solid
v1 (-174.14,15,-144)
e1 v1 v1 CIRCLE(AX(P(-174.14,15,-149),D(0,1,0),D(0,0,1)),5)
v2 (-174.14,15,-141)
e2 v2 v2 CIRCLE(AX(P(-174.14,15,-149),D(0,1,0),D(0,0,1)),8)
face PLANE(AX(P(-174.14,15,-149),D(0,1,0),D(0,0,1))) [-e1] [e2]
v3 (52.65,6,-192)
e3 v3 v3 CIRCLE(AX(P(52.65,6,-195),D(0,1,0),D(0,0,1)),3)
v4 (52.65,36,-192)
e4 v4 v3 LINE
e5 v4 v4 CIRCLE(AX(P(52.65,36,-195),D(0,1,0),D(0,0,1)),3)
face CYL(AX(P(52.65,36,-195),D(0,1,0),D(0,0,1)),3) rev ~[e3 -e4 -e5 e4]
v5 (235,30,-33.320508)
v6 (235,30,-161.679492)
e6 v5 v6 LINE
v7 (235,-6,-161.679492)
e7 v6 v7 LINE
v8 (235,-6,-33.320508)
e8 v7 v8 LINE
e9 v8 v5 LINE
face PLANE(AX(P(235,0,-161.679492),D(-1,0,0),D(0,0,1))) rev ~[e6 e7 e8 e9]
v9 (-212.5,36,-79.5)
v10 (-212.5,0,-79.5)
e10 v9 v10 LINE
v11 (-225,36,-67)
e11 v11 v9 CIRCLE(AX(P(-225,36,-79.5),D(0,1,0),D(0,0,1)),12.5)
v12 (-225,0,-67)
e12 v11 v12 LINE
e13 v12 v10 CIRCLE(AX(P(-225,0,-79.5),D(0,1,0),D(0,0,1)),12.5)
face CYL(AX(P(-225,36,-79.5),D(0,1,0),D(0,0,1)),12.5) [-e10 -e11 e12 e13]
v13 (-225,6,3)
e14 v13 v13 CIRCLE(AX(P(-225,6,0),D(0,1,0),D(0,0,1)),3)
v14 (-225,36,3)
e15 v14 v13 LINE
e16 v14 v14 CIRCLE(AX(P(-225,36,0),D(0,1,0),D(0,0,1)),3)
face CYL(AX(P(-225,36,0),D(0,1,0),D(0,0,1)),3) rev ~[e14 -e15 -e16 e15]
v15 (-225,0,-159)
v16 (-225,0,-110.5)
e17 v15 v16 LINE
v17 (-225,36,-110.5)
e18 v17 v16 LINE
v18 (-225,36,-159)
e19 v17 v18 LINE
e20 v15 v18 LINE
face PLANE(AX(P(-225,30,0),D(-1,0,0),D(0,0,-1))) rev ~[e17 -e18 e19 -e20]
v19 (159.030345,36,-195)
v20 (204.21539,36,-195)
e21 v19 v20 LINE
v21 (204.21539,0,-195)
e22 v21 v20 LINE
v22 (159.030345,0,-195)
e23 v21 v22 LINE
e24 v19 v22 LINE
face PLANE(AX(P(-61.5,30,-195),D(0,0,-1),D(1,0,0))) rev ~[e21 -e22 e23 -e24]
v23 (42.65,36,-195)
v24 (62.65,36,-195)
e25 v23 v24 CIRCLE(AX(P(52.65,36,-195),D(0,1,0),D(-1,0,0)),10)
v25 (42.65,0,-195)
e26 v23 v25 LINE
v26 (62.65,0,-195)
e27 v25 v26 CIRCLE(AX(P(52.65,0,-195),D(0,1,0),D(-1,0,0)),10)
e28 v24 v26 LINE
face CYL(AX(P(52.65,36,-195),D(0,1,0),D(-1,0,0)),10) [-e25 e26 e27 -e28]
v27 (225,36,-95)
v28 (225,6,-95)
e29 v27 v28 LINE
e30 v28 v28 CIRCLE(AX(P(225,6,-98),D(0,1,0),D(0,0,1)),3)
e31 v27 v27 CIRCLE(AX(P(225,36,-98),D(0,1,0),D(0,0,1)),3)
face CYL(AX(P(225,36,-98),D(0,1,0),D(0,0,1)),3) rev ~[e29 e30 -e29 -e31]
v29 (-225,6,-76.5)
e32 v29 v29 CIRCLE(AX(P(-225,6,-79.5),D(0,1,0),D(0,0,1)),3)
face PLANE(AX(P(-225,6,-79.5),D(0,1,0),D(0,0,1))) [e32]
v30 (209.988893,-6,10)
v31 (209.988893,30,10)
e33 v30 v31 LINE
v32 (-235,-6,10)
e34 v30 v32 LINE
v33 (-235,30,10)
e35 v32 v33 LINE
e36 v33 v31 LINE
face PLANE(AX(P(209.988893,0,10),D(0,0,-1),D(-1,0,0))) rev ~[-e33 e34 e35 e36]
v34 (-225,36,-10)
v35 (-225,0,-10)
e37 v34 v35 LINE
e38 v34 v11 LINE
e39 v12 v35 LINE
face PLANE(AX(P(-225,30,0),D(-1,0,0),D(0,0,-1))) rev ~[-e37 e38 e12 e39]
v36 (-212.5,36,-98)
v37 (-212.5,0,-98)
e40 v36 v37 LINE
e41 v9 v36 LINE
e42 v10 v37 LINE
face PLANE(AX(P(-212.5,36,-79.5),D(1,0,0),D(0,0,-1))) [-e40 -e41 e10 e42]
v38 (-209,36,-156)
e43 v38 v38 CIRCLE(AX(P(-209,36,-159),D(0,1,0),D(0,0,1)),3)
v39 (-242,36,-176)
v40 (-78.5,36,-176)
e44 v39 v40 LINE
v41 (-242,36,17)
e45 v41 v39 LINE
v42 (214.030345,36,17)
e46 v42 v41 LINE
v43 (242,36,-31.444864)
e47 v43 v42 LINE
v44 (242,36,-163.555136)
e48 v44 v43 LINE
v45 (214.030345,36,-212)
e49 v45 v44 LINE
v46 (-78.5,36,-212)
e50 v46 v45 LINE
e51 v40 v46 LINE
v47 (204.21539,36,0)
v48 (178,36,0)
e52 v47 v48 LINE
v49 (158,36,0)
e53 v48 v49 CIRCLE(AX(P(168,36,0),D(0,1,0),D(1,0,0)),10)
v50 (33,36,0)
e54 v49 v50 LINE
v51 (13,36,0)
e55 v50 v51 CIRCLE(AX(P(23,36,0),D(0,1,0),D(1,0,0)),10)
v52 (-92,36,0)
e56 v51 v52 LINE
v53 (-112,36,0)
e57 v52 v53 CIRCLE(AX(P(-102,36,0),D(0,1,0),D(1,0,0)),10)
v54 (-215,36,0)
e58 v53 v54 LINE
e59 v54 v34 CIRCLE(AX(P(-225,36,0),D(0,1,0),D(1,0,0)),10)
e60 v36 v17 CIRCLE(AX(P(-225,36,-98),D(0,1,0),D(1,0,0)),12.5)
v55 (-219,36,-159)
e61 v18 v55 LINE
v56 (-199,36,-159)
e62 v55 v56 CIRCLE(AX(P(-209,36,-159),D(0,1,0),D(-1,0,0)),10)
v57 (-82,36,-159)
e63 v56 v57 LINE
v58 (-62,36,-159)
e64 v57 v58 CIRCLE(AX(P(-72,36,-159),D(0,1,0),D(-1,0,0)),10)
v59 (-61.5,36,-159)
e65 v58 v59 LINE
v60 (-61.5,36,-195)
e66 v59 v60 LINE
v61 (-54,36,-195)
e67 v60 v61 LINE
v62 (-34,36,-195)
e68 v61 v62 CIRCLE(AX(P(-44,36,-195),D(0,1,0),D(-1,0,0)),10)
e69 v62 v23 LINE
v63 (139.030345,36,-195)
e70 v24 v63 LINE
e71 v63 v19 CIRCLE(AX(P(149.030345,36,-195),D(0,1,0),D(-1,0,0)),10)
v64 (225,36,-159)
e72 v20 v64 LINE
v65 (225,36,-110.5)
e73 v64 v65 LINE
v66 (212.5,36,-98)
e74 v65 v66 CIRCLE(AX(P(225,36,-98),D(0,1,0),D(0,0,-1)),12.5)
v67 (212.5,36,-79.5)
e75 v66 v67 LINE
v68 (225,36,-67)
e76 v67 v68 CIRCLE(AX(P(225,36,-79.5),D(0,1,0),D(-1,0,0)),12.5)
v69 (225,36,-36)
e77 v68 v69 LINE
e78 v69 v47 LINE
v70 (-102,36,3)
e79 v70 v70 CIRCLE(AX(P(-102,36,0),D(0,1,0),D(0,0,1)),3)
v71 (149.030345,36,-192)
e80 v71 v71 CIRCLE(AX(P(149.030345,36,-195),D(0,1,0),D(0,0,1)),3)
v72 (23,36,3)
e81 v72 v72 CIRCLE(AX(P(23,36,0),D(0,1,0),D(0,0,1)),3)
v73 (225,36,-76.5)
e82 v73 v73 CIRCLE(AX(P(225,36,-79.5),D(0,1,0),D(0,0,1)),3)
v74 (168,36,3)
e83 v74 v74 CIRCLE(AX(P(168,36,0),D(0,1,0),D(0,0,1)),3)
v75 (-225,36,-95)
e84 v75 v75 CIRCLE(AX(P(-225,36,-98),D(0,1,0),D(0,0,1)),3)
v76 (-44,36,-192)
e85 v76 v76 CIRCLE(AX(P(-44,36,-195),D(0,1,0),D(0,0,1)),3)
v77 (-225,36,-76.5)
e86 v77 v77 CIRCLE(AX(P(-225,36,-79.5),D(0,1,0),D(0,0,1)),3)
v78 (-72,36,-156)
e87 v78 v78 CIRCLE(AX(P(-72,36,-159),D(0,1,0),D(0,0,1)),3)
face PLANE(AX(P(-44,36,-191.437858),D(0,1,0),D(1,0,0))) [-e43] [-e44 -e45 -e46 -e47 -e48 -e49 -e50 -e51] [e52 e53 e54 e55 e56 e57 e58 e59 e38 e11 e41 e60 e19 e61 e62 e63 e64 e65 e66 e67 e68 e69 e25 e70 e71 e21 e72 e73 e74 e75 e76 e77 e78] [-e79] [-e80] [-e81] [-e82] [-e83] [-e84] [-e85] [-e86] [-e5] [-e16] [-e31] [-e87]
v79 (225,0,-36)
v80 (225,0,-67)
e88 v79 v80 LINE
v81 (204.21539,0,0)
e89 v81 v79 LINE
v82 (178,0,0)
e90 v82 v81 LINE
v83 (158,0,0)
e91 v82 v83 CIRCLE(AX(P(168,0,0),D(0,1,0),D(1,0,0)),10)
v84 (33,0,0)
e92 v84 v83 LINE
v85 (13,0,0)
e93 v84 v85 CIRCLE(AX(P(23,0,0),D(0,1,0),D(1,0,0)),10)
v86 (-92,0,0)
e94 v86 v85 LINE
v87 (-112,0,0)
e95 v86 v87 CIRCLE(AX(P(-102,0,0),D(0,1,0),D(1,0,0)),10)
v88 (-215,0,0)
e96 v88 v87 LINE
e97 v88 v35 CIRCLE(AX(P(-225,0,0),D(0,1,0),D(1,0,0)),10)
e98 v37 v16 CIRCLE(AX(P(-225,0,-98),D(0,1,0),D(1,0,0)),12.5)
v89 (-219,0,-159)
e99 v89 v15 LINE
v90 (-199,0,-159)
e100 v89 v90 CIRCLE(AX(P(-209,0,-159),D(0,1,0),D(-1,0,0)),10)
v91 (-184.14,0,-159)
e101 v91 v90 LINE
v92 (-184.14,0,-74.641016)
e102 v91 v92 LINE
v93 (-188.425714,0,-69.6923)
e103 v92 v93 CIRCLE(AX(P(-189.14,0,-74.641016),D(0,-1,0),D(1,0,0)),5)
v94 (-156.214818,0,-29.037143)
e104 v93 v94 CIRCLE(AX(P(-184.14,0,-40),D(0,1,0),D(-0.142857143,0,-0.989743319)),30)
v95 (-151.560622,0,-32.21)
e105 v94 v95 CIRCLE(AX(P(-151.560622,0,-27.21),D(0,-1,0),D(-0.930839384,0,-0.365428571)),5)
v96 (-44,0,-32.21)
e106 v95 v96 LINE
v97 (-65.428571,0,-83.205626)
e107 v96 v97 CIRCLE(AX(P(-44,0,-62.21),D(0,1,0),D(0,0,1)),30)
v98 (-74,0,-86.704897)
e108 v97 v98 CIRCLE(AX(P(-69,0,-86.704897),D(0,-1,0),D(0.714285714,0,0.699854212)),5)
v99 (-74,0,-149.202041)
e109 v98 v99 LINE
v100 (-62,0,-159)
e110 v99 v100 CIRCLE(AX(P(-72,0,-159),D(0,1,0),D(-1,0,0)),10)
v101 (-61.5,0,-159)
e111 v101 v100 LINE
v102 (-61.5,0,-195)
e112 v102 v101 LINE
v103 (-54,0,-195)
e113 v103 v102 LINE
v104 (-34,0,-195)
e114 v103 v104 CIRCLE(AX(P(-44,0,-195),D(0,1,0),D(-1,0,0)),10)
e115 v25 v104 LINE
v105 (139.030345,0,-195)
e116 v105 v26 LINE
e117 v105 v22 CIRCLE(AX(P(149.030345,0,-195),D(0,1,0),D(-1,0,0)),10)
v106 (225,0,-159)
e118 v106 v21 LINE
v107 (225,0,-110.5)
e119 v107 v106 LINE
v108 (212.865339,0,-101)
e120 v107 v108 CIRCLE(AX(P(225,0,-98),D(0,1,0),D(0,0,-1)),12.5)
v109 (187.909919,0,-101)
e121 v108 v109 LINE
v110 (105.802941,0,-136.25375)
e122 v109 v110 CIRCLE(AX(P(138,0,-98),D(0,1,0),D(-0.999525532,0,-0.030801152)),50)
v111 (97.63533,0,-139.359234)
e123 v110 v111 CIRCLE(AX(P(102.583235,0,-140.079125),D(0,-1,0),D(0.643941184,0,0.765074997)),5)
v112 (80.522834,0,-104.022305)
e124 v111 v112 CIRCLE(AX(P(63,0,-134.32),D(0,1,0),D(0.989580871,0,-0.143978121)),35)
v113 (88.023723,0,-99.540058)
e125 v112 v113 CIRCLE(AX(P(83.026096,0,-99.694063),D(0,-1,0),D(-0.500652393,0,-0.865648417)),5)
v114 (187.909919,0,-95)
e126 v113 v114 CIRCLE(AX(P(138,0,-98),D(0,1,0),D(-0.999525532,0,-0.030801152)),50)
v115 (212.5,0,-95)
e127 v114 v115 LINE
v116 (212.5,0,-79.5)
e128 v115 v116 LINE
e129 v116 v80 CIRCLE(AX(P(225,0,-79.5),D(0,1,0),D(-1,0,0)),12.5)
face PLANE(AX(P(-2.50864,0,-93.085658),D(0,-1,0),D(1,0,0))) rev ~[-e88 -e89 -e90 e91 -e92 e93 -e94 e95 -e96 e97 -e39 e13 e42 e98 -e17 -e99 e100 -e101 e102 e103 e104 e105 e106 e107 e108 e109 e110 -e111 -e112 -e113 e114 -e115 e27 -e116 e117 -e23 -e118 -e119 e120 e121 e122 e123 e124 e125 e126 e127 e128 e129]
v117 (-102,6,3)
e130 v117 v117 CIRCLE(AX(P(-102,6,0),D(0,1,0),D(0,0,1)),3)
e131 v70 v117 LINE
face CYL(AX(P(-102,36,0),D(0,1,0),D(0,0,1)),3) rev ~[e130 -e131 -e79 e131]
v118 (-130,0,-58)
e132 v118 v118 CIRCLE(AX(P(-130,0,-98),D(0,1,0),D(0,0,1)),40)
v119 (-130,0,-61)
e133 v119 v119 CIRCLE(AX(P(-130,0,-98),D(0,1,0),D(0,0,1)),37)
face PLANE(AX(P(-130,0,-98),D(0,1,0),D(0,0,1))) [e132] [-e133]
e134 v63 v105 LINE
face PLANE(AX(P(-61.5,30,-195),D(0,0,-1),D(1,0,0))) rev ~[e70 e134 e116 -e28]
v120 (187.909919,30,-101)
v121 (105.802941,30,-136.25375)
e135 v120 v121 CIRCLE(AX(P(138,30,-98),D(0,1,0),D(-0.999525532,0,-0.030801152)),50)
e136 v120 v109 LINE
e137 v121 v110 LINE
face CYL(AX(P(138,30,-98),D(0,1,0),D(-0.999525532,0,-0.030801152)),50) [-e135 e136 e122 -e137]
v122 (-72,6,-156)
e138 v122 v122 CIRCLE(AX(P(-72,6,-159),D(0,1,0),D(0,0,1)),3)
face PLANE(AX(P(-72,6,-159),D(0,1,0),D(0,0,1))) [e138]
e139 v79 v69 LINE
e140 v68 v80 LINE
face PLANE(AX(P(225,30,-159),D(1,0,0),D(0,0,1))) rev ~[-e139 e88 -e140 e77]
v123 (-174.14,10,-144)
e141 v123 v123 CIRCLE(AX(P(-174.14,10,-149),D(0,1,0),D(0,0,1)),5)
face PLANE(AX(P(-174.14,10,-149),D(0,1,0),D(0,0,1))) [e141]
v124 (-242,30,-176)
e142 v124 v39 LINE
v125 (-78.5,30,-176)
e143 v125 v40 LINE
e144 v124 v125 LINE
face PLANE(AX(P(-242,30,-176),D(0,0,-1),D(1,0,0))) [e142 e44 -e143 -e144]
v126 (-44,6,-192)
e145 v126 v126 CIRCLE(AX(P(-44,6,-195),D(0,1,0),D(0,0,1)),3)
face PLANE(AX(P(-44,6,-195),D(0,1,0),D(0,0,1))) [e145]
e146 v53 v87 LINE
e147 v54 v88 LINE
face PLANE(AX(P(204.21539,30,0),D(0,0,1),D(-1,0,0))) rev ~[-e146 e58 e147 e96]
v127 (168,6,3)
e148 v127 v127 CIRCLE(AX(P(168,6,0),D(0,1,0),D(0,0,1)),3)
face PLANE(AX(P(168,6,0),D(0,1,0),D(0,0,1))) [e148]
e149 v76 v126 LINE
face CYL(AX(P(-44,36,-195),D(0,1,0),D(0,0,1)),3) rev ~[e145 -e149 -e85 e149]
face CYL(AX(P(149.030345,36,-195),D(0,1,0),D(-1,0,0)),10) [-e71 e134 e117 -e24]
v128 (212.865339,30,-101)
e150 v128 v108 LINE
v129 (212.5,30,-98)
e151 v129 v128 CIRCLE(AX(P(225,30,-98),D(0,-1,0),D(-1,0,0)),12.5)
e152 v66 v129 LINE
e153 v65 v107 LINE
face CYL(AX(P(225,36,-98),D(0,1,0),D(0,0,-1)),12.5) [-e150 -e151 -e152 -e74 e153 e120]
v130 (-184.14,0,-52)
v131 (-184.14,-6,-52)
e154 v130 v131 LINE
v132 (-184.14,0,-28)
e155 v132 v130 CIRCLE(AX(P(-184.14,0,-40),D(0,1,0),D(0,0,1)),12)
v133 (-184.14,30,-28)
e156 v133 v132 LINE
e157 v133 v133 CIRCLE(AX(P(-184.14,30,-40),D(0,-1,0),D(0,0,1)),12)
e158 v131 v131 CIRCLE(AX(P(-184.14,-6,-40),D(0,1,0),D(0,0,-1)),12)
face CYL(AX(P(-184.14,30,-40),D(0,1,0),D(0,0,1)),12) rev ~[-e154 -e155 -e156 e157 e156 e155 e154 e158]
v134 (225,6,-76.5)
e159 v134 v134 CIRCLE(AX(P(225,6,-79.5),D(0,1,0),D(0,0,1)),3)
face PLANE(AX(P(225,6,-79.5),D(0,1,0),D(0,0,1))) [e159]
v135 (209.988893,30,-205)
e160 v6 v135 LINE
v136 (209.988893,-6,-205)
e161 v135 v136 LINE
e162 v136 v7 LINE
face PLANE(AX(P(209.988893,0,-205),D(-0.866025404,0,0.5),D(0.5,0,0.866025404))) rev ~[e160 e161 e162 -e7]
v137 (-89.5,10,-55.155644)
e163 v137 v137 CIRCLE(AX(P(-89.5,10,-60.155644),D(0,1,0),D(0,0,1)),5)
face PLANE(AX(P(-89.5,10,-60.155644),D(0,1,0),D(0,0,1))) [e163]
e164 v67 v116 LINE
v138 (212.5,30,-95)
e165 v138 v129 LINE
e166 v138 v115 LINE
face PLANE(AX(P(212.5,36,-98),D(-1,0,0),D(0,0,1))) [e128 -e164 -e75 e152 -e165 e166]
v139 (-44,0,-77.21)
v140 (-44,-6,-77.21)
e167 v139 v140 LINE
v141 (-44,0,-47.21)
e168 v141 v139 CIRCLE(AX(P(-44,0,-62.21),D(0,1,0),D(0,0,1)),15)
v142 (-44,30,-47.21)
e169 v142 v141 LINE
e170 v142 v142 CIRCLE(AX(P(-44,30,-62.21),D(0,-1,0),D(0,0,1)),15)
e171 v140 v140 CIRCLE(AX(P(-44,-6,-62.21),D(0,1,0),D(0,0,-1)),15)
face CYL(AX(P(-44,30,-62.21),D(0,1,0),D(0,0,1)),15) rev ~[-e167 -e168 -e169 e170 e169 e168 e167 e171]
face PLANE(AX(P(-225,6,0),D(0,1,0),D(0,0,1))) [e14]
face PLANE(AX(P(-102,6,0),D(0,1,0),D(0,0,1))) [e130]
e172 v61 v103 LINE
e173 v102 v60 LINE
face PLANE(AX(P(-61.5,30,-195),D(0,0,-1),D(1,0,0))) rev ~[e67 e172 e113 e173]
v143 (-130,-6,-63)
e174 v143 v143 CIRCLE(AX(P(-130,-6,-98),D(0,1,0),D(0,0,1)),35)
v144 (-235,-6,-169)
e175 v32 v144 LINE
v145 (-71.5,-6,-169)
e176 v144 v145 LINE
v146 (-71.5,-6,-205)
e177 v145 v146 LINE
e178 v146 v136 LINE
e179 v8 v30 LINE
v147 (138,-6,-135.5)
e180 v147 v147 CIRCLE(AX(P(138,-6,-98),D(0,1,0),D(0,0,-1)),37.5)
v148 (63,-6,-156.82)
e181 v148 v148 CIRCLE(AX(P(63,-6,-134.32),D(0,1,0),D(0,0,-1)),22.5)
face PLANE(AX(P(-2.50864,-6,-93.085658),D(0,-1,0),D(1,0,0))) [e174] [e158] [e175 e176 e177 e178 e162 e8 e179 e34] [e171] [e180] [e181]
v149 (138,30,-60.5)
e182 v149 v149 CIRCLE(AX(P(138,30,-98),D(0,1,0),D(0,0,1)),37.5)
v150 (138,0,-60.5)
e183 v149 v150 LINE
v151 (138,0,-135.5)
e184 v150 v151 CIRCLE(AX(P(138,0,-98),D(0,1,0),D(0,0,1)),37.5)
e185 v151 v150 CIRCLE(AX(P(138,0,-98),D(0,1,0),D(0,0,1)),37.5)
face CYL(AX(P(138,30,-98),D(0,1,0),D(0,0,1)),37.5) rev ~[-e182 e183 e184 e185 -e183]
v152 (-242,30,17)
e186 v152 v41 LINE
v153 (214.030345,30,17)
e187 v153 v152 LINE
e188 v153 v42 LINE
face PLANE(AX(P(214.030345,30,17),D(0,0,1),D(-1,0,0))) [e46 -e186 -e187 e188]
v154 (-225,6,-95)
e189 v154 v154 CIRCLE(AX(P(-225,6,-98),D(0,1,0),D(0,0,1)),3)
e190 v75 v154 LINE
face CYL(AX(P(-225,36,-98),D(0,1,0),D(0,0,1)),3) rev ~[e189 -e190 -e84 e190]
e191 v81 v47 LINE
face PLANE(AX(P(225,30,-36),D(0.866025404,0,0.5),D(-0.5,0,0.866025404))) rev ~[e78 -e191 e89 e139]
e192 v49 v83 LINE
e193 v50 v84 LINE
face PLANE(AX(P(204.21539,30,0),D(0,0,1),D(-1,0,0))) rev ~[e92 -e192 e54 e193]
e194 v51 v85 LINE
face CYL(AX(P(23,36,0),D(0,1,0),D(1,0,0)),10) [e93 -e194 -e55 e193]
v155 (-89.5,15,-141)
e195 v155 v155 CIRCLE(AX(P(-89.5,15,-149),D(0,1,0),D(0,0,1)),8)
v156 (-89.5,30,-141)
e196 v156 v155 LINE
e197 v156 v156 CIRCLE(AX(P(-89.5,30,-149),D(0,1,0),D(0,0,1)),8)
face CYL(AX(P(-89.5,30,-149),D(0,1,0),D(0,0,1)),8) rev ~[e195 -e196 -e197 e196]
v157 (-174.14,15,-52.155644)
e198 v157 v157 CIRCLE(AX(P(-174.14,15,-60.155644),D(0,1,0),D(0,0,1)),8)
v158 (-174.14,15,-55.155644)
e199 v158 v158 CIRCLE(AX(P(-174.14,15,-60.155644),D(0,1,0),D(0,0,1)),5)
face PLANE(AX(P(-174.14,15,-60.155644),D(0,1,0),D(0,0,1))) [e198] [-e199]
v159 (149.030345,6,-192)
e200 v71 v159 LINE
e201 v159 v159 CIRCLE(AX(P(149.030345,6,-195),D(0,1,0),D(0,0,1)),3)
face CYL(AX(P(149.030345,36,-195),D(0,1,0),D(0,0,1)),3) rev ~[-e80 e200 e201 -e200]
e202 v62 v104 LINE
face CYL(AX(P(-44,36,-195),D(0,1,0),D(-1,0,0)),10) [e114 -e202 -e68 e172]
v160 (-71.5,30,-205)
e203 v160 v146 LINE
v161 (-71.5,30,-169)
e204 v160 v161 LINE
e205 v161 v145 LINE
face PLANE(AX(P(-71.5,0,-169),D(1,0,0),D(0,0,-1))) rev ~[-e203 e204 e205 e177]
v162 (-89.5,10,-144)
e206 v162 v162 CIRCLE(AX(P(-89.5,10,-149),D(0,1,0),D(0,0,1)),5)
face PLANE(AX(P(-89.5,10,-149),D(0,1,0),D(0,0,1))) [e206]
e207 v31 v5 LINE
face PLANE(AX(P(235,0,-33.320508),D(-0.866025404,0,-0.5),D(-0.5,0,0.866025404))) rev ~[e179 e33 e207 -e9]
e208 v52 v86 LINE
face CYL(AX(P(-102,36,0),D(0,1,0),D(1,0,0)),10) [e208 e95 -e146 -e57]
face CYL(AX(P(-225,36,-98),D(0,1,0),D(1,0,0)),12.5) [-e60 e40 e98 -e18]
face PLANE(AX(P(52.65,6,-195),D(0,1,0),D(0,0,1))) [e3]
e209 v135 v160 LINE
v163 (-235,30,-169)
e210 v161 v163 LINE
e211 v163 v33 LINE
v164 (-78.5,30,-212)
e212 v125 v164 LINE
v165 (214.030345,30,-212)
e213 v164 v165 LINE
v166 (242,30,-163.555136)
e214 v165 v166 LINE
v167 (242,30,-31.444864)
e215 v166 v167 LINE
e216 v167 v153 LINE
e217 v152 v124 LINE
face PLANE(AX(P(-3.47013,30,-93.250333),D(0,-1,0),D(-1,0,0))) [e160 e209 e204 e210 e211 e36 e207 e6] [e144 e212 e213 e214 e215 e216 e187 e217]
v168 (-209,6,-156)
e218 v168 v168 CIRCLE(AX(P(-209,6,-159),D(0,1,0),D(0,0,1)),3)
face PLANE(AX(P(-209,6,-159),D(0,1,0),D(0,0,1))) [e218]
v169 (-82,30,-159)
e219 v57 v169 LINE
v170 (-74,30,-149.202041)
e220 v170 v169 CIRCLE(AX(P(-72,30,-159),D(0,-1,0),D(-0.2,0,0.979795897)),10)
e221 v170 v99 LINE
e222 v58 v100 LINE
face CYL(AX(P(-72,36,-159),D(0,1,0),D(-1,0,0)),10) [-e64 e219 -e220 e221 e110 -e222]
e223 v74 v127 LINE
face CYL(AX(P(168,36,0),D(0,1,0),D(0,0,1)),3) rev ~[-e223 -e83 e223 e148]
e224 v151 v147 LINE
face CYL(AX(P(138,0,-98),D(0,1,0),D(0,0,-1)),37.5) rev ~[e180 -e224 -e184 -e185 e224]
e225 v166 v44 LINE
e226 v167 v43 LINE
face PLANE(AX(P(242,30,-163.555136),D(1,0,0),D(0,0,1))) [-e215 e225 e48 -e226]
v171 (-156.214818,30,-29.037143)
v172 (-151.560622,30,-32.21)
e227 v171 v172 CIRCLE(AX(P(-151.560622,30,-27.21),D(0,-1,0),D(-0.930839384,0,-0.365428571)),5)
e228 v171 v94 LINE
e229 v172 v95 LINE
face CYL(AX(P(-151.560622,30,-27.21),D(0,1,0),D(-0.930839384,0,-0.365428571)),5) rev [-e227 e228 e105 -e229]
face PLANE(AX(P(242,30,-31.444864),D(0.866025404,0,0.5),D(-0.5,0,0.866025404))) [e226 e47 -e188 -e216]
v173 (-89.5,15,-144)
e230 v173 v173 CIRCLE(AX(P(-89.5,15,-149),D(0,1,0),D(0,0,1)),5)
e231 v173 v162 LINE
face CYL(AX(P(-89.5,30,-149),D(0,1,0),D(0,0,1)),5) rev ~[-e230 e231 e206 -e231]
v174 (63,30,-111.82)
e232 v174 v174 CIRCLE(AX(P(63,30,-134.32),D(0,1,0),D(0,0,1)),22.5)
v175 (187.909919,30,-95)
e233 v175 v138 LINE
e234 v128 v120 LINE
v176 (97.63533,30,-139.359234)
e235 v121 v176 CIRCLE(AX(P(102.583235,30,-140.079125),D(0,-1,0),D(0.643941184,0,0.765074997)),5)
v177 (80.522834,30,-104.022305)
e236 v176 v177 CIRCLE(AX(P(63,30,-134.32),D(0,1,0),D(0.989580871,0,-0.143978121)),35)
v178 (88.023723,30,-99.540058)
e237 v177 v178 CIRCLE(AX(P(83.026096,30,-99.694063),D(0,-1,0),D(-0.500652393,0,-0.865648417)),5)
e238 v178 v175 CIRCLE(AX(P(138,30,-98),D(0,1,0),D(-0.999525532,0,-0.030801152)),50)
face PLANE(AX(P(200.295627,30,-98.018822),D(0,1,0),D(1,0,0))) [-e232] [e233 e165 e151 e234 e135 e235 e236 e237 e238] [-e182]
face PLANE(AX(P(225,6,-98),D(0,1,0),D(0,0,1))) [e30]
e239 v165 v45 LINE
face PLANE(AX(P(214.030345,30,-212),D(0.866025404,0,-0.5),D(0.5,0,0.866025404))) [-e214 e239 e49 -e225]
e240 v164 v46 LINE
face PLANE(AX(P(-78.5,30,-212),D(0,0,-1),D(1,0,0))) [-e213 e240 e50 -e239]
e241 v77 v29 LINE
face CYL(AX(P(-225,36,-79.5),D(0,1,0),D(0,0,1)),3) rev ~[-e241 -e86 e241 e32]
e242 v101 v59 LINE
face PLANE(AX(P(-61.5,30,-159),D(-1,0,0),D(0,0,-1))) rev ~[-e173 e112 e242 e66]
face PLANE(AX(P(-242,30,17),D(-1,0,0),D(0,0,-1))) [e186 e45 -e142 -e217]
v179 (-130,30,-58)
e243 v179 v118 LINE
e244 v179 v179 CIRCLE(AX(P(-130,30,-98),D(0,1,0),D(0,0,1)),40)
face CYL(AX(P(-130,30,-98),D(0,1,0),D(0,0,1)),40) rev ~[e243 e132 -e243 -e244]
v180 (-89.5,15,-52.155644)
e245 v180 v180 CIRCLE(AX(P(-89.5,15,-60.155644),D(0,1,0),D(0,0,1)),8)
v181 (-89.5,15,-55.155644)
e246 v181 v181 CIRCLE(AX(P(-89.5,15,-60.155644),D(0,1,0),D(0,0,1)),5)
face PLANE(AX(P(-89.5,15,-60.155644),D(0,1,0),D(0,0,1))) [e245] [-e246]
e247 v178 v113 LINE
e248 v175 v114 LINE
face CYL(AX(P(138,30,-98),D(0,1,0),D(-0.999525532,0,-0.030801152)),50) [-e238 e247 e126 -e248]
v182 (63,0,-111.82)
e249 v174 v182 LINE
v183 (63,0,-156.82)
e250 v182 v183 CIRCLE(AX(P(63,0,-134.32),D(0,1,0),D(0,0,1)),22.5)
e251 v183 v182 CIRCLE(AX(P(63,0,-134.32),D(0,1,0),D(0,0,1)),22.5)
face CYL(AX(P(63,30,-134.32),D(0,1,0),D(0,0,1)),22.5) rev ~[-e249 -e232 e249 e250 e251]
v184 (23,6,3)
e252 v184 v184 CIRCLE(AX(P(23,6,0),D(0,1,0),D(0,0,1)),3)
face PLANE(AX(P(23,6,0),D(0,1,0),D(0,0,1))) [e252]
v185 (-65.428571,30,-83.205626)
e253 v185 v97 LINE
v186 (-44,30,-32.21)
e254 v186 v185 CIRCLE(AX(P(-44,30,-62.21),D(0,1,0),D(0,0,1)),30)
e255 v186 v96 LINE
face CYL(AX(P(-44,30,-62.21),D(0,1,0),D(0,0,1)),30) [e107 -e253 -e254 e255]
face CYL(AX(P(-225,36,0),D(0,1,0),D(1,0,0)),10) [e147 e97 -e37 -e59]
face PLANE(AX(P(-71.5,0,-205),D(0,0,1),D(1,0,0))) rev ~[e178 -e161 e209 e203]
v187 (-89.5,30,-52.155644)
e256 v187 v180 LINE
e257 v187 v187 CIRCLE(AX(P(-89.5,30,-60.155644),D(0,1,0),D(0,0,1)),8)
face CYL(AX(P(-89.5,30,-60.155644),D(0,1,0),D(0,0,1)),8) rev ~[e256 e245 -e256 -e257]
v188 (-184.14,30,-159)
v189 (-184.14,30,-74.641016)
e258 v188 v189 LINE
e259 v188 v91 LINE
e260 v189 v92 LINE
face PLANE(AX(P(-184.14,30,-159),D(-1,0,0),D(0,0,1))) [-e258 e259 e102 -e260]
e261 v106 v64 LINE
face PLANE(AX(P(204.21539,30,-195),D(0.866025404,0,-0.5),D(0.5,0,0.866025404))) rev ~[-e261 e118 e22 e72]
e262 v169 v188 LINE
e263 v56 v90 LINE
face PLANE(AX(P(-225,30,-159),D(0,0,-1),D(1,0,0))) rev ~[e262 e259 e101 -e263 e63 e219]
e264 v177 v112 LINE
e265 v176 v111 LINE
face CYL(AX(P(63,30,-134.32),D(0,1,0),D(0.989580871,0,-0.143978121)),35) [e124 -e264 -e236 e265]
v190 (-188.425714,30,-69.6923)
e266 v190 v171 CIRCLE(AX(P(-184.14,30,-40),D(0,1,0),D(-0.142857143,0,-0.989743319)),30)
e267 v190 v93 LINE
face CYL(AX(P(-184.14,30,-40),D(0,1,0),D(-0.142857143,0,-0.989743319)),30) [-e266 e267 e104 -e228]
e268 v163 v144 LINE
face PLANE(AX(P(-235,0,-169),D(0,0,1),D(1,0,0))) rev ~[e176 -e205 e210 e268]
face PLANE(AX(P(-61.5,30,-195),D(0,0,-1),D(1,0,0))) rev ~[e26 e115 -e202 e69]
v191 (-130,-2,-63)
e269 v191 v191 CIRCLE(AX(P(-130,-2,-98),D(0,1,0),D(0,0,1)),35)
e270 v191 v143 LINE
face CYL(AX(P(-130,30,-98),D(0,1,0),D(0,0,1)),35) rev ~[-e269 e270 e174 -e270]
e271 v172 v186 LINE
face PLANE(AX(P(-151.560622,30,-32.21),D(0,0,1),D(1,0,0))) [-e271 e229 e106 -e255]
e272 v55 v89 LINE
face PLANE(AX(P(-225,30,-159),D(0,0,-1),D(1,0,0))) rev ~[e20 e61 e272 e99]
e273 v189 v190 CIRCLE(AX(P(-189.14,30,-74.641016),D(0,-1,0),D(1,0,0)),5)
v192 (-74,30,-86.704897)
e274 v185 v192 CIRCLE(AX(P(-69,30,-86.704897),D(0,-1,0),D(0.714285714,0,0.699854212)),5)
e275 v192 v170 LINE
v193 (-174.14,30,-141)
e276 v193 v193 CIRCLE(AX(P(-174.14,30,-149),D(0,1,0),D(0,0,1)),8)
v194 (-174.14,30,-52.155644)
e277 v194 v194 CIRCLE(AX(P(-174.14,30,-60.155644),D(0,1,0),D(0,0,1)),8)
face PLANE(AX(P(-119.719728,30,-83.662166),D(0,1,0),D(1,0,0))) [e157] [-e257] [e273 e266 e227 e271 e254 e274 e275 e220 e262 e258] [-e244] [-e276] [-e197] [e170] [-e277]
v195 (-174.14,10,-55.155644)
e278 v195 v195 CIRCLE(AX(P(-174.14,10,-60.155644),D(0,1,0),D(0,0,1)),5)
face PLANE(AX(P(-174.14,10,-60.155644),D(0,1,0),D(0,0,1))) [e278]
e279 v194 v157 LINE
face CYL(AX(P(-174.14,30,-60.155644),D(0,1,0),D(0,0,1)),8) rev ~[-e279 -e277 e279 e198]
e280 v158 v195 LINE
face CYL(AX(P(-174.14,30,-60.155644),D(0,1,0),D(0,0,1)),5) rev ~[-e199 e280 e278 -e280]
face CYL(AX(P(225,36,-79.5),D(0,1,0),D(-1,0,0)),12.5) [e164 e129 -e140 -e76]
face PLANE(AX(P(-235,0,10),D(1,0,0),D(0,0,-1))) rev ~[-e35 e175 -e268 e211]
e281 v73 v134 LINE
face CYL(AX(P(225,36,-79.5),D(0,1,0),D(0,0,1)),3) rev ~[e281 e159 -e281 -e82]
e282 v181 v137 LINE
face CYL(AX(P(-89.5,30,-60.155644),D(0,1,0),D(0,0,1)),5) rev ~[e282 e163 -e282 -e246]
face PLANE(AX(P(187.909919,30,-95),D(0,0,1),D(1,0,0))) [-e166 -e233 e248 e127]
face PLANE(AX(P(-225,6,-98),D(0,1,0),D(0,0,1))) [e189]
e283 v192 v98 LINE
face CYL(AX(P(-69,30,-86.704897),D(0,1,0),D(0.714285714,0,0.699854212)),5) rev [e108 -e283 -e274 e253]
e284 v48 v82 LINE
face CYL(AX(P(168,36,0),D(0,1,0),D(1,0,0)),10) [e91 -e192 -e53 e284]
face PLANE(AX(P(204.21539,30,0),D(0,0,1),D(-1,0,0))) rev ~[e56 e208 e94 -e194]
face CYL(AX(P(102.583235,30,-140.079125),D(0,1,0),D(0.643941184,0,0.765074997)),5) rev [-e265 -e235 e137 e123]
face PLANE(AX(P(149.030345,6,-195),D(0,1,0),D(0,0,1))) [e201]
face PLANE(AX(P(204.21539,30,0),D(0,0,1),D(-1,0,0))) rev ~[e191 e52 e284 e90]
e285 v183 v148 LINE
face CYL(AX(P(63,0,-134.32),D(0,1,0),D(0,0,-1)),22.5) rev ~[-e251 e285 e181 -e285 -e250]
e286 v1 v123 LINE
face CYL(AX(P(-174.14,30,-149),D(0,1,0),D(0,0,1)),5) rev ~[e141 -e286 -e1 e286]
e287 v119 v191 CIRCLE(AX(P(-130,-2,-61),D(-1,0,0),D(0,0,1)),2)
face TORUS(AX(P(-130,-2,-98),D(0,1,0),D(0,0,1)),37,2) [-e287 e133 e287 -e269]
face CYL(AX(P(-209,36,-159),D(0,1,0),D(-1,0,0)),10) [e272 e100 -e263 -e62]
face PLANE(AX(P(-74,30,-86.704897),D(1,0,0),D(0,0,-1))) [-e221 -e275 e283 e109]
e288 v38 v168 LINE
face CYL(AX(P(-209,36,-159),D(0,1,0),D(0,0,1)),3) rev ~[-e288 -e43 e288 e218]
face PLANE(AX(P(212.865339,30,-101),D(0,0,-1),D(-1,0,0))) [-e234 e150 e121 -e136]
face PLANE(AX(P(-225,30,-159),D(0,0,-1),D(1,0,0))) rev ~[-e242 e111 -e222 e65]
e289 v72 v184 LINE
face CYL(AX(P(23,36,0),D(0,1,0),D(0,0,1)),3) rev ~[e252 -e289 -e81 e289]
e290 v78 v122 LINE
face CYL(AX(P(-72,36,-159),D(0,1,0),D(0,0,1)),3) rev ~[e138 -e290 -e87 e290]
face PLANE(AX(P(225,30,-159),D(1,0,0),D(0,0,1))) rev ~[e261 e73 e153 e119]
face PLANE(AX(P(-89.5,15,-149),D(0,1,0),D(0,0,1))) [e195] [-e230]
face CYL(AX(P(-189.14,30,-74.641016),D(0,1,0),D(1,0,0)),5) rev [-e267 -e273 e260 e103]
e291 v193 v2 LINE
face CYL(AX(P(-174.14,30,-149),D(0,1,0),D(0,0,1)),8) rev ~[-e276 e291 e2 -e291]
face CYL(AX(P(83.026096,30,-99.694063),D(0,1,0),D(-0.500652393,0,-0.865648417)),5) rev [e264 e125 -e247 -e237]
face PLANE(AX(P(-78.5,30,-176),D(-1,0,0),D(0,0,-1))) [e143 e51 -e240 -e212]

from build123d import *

# Parameters (mm, degrees)
CASING_WALL_10MM_DEPTH      = 30
FLOOR_PLATE_6MM_DEPTH       = 6
PERIMETER_FLANGE_DEPTH      = 6
WALL_BOSSES_DEPTH           = 36
INTERIOR_POCKET_SKETCH_R    = 3
INTERIOR_POCKET_CUT_DEPTH   = 30
BEARING_START               = 30
BEARING_HOUSINGS_SKETCH_R   = 12
BEARING_HOUSINGS_SKETCH_R_2 = 15
BEARING_HOUSINGS_SKETCH_R_3 = 40
BEARING_HOUSINGS_SKETCH_R_4 = 22.5
BEARING_HOUSINGS_SKETCH_R_5 = 37.5
BEARING_HOUSINGS_DEPTH      = 30
BEARING_BORES_SKETCH_R      = 35
BEARING_BORES_SKETCH_R_2    = 12
BEARING_BORES_SKETCH_R_3    = 15
BEARING_BORES_DEPTH         = 50
SECONDARY_BORE_SKETCH_R     = 40
SECONDARY_BORE_SKETCH_R_2   = 35
SECONDARY_BORE_DEPTH        = 30
FASTENER_HOLES_SKETCH_R     = 5
FASTENER_HOLES_DEPTH        = 20
BOSS_HOLES_SKETCH_R         = 8
BOSS_HOLES_SKETCH_R_2       = 5
BOSS_HOLES_DEPTH            = 15
HOUSING_SLOT_SKETCH_R       = 22.5
HOUSING_SLOT_SKETCH_R_2     = 37.5
HOUSING_SLOT_CUT_DEPTH      = 30
BORE_EDGE_FILLET_R2_R       = 2


with BuildPart() as part:
    # Casing Outline Sketch → Casing Wall 10mm (new body)
    with BuildSketch(Plane(origin=(0, 0, 0), x_dir=(1, 0, 0), z_dir=(0, 1, 0))):
        Polygon((235, 33.320508076), (235, 161.679491924), (209.988893001, 205), (-71.5, 205), (-71.5, 169), (-235, 169), (-235, -10), (209.988893001, -10), align=None)
        Polygon((225, 36), (225, 159), (204.215390309, 195), (-61.5, 195), (-61.5, 159), (-225, 159), (-225, 0), (204.215390309, 0), align=None, mode=Mode.SUBTRACT)
    extrude(amount=CASING_WALL_10MM_DEPTH)

    # Floor Plate Sketch → Floor Plate 6mm (add)
    with BuildSketch(Plane.XZ):
        Polygon((-235, 10), (-235, -169), (-71.5, -169), (-71.5, -205), (209.988893001, -205), (235, -161.679491924), (235, -33.320508076), (209.988893001, 10), align=None)
    extrude(amount=FLOOR_PLATE_6MM_DEPTH)

    # Perimeter Flange Sketch → Perimeter Flange (add)
    with BuildSketch(Plane(origin=(0, 30, 0), x_dir=(1, 0, 0), z_dir=(0, 1, 0))):
        Polygon((-242, 176), (-78.5, 176), (-78.5, 212), (214.030344885, 212), (242, 163.555136271), (242, 31.444863729), (214.030344885, -17), (-242, -17), align=None)
        Polygon((-225, 0), (-225, 159), (-61.5, 159), (-61.5, 195), (204.215390309, 195), (225, 159), (225, 36), (204.215390309, 0), align=None, mode=Mode.SUBTRACT)
    extrude(amount=PERIMETER_FLANGE_DEPTH)

    # Wall Bosses Sketch → Wall Bosses (add)
    with BuildSketch(Plane(origin=(0, 36, 0), x_dir=(1, 0, 0), z_dir=(0, 1, 0))):
        with BuildLine():
            ThreePointArc((-54, 195), (-44, 185), (-34, 195))
            Line((-34, 195), (-41, 195))
            ThreePointArc((-41, 195), (-44, 192), (-47, 195))
            Line((-47, 195), (-54, 195))
        make_face()
        with BuildLine():
            Line((-47, 195), (-41, 195))
            ThreePointArc((-41, 195), (-44, 198), (-47, 195))
        make_face()
        with BuildLine():
            ThreePointArc((-47, 195), (-44, 192), (-41, 195))
            Line((-41, 195), (-47, 195))
        make_face()
        with BuildLine():
            ThreePointArc((42.65, 195), (52.65, 185), (62.65, 195))
            Line((62.65, 195), (55.65, 195))
            ThreePointArc((55.65, 195), (52.65, 192), (49.65, 195))
            Line((49.65, 195), (42.65, 195))
        make_face()
        with BuildLine():
            Line((49.65, 195), (55.65, 195))
            ThreePointArc((55.65, 195), (52.65, 198), (49.65, 195))
        make_face()
        with BuildLine():
            ThreePointArc((49.65, 195), (52.65, 192), (55.65, 195))
            Line((55.65, 195), (49.65, 195))
        make_face()
        with BuildLine():
            ThreePointArc((139.030344885, 195), (149.030344885, 185), (159.030344885, 195))
            Line((159.030344885, 195), (152.030344885, 195))
            ThreePointArc((152.030344885, 195), (149.030344885, 192), (146.030344885, 195))
            Line((146.030344885, 195), (139.030344885, 195))
        make_face()
        with BuildLine():
            Line((146.030344885, 195), (152.030344885, 195))
            ThreePointArc((152.030344885, 195), (149.030344885, 198), (146.030344885, 195))
        make_face()
        with BuildLine():
            ThreePointArc((146.030344885, 195), (149.030344885, 192), (152.030344885, 195))
            Line((152.030344885, 195), (146.030344885, 195))
        make_face()
        with BuildLine():
            ThreePointArc((212.5, 79.5), (216.161165235, 70.661165235), (225, 67))
            Line((225, 67), (225, 76.5))
            ThreePointArc((225, 76.5), (222, 79.5), (225, 82.5))
            Line((225, 82.5), (225, 95))
            ThreePointArc((225, 95), (222, 98), (225, 101))
            Line((225, 101), (225, 110.5))
            ThreePointArc((225, 110.5), (216.161165235, 106.838834765), (212.5, 98))
            Line((212.5, 98), (212.5, 79.5))
        make_face()
        with BuildLine():
            Line((225, 101), (225, 95))
            ThreePointArc((225, 95), (227.121320344, 95.878679656), (228, 98))
            ThreePointArc((228, 98), (227.121320344, 100.121320344), (225, 101))
        make_face()
        with BuildLine():
            ThreePointArc((225, 101), (222, 98), (225, 95))
            Line((225, 95), (225, 101))
        make_face()
        with BuildLine():
            Line((225, 82.5), (225, 76.5))
            ThreePointArc((225, 76.5), (227.121320344, 77.378679656), (228, 79.5))
            ThreePointArc((228, 79.5), (227.121320344, 81.621320344), (225, 82.5))
        make_face()
        with BuildLine():
            ThreePointArc((225, 82.5), (222, 79.5), (225, 76.5))
            Line((225, 76.5), (225, 82.5))
        make_face()
        with BuildLine():
            Line((-212, 159), (-219, 159))
            ThreePointArc((-219, 159), (-209, 149), (-199, 159))
            Line((-199, 159), (-206, 159))
            ThreePointArc((-206, 159), (-209, 156), (-212, 159))
        make_face()
        with BuildLine():
            Line((-206, 159), (-212, 159))
            ThreePointArc((-212, 159), (-209, 156), (-206, 159))
        make_face()
        with BuildLine():
            ThreePointArc((-206, 159), (-209, 162), (-212, 159))
            Line((-212, 159), (-206, 159))
        make_face()
        with BuildLine():
            Line((-69, 159), (-75, 159))
            ThreePointArc((-75, 159), (-72, 156), (-69, 159))
        make_face()
        with BuildLine():
            ThreePointArc((-69, 159), (-72, 162), (-75, 159))
            Line((-75, 159), (-69, 159))
        make_face()
        with BuildLine():
            Line((-75, 159), (-82, 159))
            ThreePointArc((-82, 159), (-72, 149), (-62, 159))
            Line((-62, 159), (-69, 159))
            ThreePointArc((-69, 159), (-72, 156), (-75, 159))
        make_face()
        with BuildLine():
            Line((-225, 95), (-225, 101))
            ThreePointArc((-225, 101), (-228, 98), (-225, 95))
        make_face()
        with BuildLine():
            ThreePointArc((-222, 98), (-222.878679656, 100.121320344), (-225, 101))
            Line((-225, 101), (-225, 95))
            ThreePointArc((-225, 95), (-222.878679656, 95.878679656), (-222, 98))
        make_face()
        with BuildLine():
            Line((-225, 76.5), (-225, 82.5))
            ThreePointArc((-225, 82.5), (-228, 79.5), (-225, 76.5))
        make_face()
        with BuildLine():
            ThreePointArc((-222, 79.5), (-222.878679656, 81.621320344), (-225, 82.5))
            Line((-225, 82.5), (-225, 76.5))
            ThreePointArc((-225, 76.5), (-222.878679656, 77.378679656), (-222, 79.5))
        make_face()
        with BuildLine():
            ThreePointArc((-212.5, 98), (-216.161165235, 106.838834765), (-225, 110.5))
            Line((-225, 110.5), (-225, 101))
            ThreePointArc((-225, 101), (-222.878679656, 100.121320344), (-222, 98))
            ThreePointArc((-222, 98), (-222.878679656, 95.878679656), (-225, 95))
            Line((-225, 95), (-225, 82.5))
            ThreePointArc((-225, 82.5), (-222.878679656, 81.621320344), (-222, 79.5))
            ThreePointArc((-222, 79.5), (-222.878679656, 77.378679656), (-225, 76.5))
            Line((-225, 76.5), (-225, 67))
            ThreePointArc((-225, 67), (-216.161165235, 70.661165235), (-212.5, 79.5))
            Line((-212.5, 79.5), (-212.5, 98))
        make_face()
        with BuildLine():
            Line((-225, 0), (-225, 3))
            ThreePointArc((-225, 3), (-227.121320344, -2.121320344), (-222, 0))
            Line((-222, 0), (-225, 0))
        make_face()
        with BuildLine():
            ThreePointArc((-222, 0), (-222.878679656, 2.121320344), (-225, 3))
            Line((-225, 3), (-225, 0))
            Line((-225, 0), (-222, 0))
        make_face()
        with BuildLine():
            ThreePointArc((-215, 0), (-217.928932188, 7.071067812), (-225, 10))
            Line((-225, 10), (-225, 3))
            ThreePointArc((-225, 3), (-222.878679656, 2.121320344), (-222, 0))
            Line((-222, 0), (-215, 0))
        make_face()
        with BuildLine():
            Line((-99, 0), (-105, 0))
            ThreePointArc((-105, 0), (-102, -3), (-99, 0))
        make_face()
        with BuildLine():
            ThreePointArc((-99, 0), (-102, 3), (-105, 0))
            Line((-105, 0), (-99, 0))
        make_face()
        with BuildLine():
            ThreePointArc((-92, 0), (-102, 10), (-112, 0))
            Line((-112, 0), (-105, 0))
            ThreePointArc((-105, 0), (-102, 3), (-99, 0))
            Line((-99, 0), (-92, 0))
        make_face()
        with BuildLine():
            ThreePointArc((33, 0), (23, 10), (13, 0))
            Line((13, 0), (20, 0))
            ThreePointArc((20, 0), (23, 3), (26, 0))
            Line((26, 0), (33, 0))
        make_face()
        with BuildLine():
            Line((26, 0), (20, 0))
            ThreePointArc((20, 0), (23, -3), (26, 0))
        make_face()
        with BuildLine():
            ThreePointArc((26, 0), (23, 3), (20, 0))
            Line((20, 0), (26, 0))
        make_face()
        with BuildLine():
            ThreePointArc((178, 0), (168, 10), (158, 0))
            Line((158, 0), (165, 0))
            ThreePointArc((165, 0), (168, 3), (171, 0))
            Line((171, 0), (178, 0))
        make_face()
        with BuildLine():
            Line((171, 0), (165, 0))
            ThreePointArc((165, 0), (168, -3), (171, 0))
        make_face()
        with BuildLine():
            ThreePointArc((171, 0), (168, 3), (165, 0))
            Line((165, 0), (171, 0))
        make_face()
    extrude(amount=-WALL_BOSSES_DEPTH)

    # Interior Pocket Sketch → Interior Pocket Cut (cut)
    with BuildSketch(Plane(origin=(0, 36, 0), x_dir=(1, 0, 0), z_dir=(0, 1, 0))):
        with Locations(Location((-209, 159, 0), (0, 0, 270))):
            Circle(INTERIOR_POCKET_SKETCH_R)
        with Locations(Location((-72, 159, 0), (0, 0, 270))):
            Circle(INTERIOR_POCKET_SKETCH_R)
        with Locations(Location((-44, 195, 0), (0, 0, 270))):
            Circle(INTERIOR_POCKET_SKETCH_R)
        with Locations(Location((52.65, 195, 0), (0, 0, 270))):
            Circle(INTERIOR_POCKET_SKETCH_R)
        with Locations(Location((149.030344885, 195, 0), (0, 0, 270))):
            Circle(INTERIOR_POCKET_SKETCH_R)
        with Locations(Location((225, 98, 0), (0, 0, 270))):
            Circle(INTERIOR_POCKET_SKETCH_R)
        with Locations(Location((225, 79.5, 0), (0, 0, 270))):
            Circle(INTERIOR_POCKET_SKETCH_R)
        with Locations(Location((168, 0, 0), (0, 0, 270))):
            Circle(INTERIOR_POCKET_SKETCH_R)
        with Locations(Location((23, 0, 0), (0, 0, 270))):
            Circle(INTERIOR_POCKET_SKETCH_R)
        with Locations(Location((-225, 98, 0), (0, 0, 270))):
            Circle(INTERIOR_POCKET_SKETCH_R)
        with Locations(Location((-225, 79.5, 0), (0, 0, 270))):
            Circle(INTERIOR_POCKET_SKETCH_R)
        with Locations(Location((-225, 0, 0), (0, 0, 270))):
            Circle(INTERIOR_POCKET_SKETCH_R)
        with Locations(Location((-102, 0, 0), (0, 0, 270))):
            Circle(INTERIOR_POCKET_SKETCH_R)
    extrude(amount=-INTERIOR_POCKET_CUT_DEPTH, mode=Mode.SUBTRACT)

    # Bearing Housings Sketch → Bearing Housings (add)
    # profile 1 of 4: a face of its own
    with BuildSketch(Plane(origin=(0, 0, 0), x_dir=(1, 0, 0), z_dir=(0, 1, 0)).offset(BEARING_START)):
        with BuildLine():
            ThreePointArc((-65.428571429, 83.205626367), (-70.889822365, 82.075796929), (-74, 86.704897428))
            Line((-74, 86.704897428), (-74, 149.202041029))
            ThreePointArc((-74, 149.202041029), (-79.745966692, 152.67544468), (-82, 159))
            Line((-82, 159), (-184.14, 159))
            Line((-184.14, 159), (-184.14, 74.641016151))
            ThreePointArc((-184.14, 74.641016151), (-185.36035527, 71.367747798), (-188.425714286, 69.692299558))
            ThreePointArc((-188.425714286, 69.692299558), (-207.65417752, 21.36982406), (-156.214818474, 29.037142857))
            ThreePointArc((-156.214818474, 29.037142857), (-154.377027571, 31.341326318), (-151.560621553, 32.21))
            Line((-151.560621553, 32.21), (-44, 32.21))
            ThreePointArc((-44, 32.21), (-16.342552621, 73.831772864), (-65.428571429, 83.205626367))
        make_face()
        with Locations(Location((-184.14, 40, 0), (0, 0, 270))):
            Circle(BEARING_HOUSINGS_SKETCH_R, mode=Mode.SUBTRACT)
        with Locations(Location((-44, 62.21, 0), (0, 0, 270))):
            Circle(BEARING_HOUSINGS_SKETCH_R_2, mode=Mode.SUBTRACT)
        with Locations((-122, 98)):
            Circle(BEARING_HOUSINGS_SKETCH_R_3, mode=Mode.SUBTRACT)
    # profile 2 of 4: a face of its own
    with BuildSketch(Plane(origin=(0, 0, 0), x_dir=(1, 0, 0), z_dir=(0, 1, 0)).offset(BEARING_START)):
        with BuildLine():
            ThreePointArc((88.023723402, 99.540057585), (183.000978656, 76.20752607), (105.802940773, 136.253749844))
            ThreePointArc((105.802940773, 136.253749844), (100.806249829, 135.405547587), (97.635330494, 139.359234225))
            ThreePointArc((97.635330494, 139.359234225), (31.499314941, 149.574731751), (80.522833774, 104.022305426))
            ThreePointArc((80.522833774, 104.022305426), (85.590876722, 103.986137262), (88.023723402, 99.540057585))
        make_face()
        with Locations(Location((63, 134.32, 0), (0, 0, 270))):
            Circle(BEARING_HOUSINGS_SKETCH_R_4, mode=Mode.SUBTRACT)
        with Locations(Location((138, 98, 0), (0, 0, 270))):
            Circle(BEARING_HOUSINGS_SKETCH_R_5, mode=Mode.SUBTRACT)
    # profile 3 of 4: a face of its own
    with BuildSketch(Plane(origin=(0, 0, 0), x_dir=(1, 0, 0), z_dir=(0, 1, 0)).offset(BEARING_START)):
        with BuildLine():
            ThreePointArc((187.909918854, 101), (188, 98), (187.909918854, 95))
            Line((187.909918854, 95), (212.5, 95))
            Line((212.5, 95), (212.5, 98))
            ThreePointArc((212.5, 98), (212.591670867, 99.511081774), (212.8653389, 101))
            Line((212.8653389, 101), (187.909918854, 101))
        make_face()
    # profile 4 of 4: a face of its own
    with BuildSketch(Plane(origin=(0, 0, 0), x_dir=(1, 0, 0), z_dir=(0, 1, 0)).offset(BEARING_START)):
        with Locations((-122, 98)):
            Circle(BEARING_HOUSINGS_SKETCH_R_3)
    extrude(amount=-BEARING_HOUSINGS_DEPTH)

    # Bearing Bores Sketch → Bearing Bores (cut)
    with BuildSketch(Plane(origin=(0, 30, 0), x_dir=(1, 0, 0), z_dir=(0, 1, 0))):
        with Locations(Location((-130, 98, 0), (0, 0, 270))):
            Circle(BEARING_BORES_SKETCH_R)
        with Locations(Location((-184.14, 40, 0), (0, 0, 90))):
            Circle(BEARING_BORES_SKETCH_R_2)
        with Locations(Location((-44, 62.21, 0), (0, 0, 90))):
            Circle(BEARING_BORES_SKETCH_R_3)
    extrude(amount=-BEARING_BORES_DEPTH, mode=Mode.SUBTRACT)

    # Secondary Bore Sketch → Secondary Bore (cut)
    with BuildSketch(Plane(origin=(0, 30, 0), x_dir=(1, 0, 0), z_dir=(0, 1, 0))):
        with Locations(Location((-130, 98, 0), (0, 0, 270))):
            Circle(SECONDARY_BORE_SKETCH_R)
        with Locations(Location((-130, 98, 0), (0, 0, 270))):
            Circle(SECONDARY_BORE_SKETCH_R_2, mode=Mode.SUBTRACT)
    extrude(amount=-SECONDARY_BORE_DEPTH, mode=Mode.SUBTRACT)

    # Fastener Holes Sketch → Fastener Holes (cut)
    with BuildSketch(Plane(origin=(0, 30, 0), x_dir=(1, 0, 0), z_dir=(0, 1, 0))):
        with Locations(Location((-174.14, 149, 0), (0, 0, 270))):
            Circle(FASTENER_HOLES_SKETCH_R)
        with Locations(Location((-89.5, 149, 0), (0, 0, 270))):
            Circle(FASTENER_HOLES_SKETCH_R)
        with Locations(Location((-89.5, 60.155644371, 0), (0, 0, 270))):
            Circle(FASTENER_HOLES_SKETCH_R)
        with Locations(Location((-174.14, 60.155644371, 0), (0, 0, 270))):
            Circle(FASTENER_HOLES_SKETCH_R)
    extrude(amount=-FASTENER_HOLES_DEPTH, mode=Mode.SUBTRACT)

    # Boss Holes Sketch → Boss Holes (cut)
    # profile 1 of 4: a face of its own
    with BuildSketch(Plane(origin=(0, 30, 0), x_dir=(1, 0, 0), z_dir=(0, 1, 0))):
        with Locations(Location((-174.14, 149, 0), (0, 0, 270))):
            Circle(BOSS_HOLES_SKETCH_R)
        with Locations(Location((-174.14, 149, 0), (0, 0, 270))):
            Circle(BOSS_HOLES_SKETCH_R_2, mode=Mode.SUBTRACT)
    # profile 2 of 4: a face of its own
    with BuildSketch(Plane(origin=(0, 30, 0), x_dir=(1, 0, 0), z_dir=(0, 1, 0))):
        with Locations(Location((-89.5, 149, 0), (0, 0, 270))):
            Circle(BOSS_HOLES_SKETCH_R)
        with Locations(Location((-89.5, 149, 0), (0, 0, 270))):
            Circle(BOSS_HOLES_SKETCH_R_2, mode=Mode.SUBTRACT)
    # profile 3 of 4: a face of its own
    with BuildSketch(Plane(origin=(0, 30, 0), x_dir=(1, 0, 0), z_dir=(0, 1, 0))):
        with Locations(Location((-174.14, 60.155644371, 0), (0, 0, 270))):
            Circle(BOSS_HOLES_SKETCH_R)
        with Locations(Location((-174.14, 60.155644371, 0), (0, 0, 270))):
            Circle(BOSS_HOLES_SKETCH_R_2, mode=Mode.SUBTRACT)
    # profile 4 of 4: a face of its own
    with BuildSketch(Plane(origin=(0, 30, 0), x_dir=(1, 0, 0), z_dir=(0, 1, 0))):
        with Locations(Location((-89.5, 60.155644371, 0), (0, 0, 270))):
            Circle(BOSS_HOLES_SKETCH_R)
        with Locations(Location((-89.5, 60.155644371, 0), (0, 0, 270))):
            Circle(BOSS_HOLES_SKETCH_R_2, mode=Mode.SUBTRACT)
    extrude(amount=-BOSS_HOLES_DEPTH, mode=Mode.SUBTRACT)

    # Housing Slot Sketch → Housing Slot Cut (cut)
    with BuildSketch(Plane(origin=(0, 0, 0), x_dir=(1, 0, 0), z_dir=(0, 1, 0))):
        with Locations(Location((63, 134.32, 0), (0, 0, 90))):
            Circle(HOUSING_SLOT_SKETCH_R)
        with Locations(Location((138, 98, 0), (0, 0, 90))):
            Circle(HOUSING_SLOT_SKETCH_R_2)
    extrude(amount=-HOUSING_SLOT_CUT_DEPTH, mode=Mode.SUBTRACT)

    # Bore Edge Fillet R2
    bore_edge_fillet_r2_edges = [part.edges().sort_by_distance(p)[0] for p in [
        (-130, 0, -133),
    ]]
    fillet(bore_edge_fillet_r2_edges, radius=BORE_EDGE_FILLET_R2_R)


solid = part.part
